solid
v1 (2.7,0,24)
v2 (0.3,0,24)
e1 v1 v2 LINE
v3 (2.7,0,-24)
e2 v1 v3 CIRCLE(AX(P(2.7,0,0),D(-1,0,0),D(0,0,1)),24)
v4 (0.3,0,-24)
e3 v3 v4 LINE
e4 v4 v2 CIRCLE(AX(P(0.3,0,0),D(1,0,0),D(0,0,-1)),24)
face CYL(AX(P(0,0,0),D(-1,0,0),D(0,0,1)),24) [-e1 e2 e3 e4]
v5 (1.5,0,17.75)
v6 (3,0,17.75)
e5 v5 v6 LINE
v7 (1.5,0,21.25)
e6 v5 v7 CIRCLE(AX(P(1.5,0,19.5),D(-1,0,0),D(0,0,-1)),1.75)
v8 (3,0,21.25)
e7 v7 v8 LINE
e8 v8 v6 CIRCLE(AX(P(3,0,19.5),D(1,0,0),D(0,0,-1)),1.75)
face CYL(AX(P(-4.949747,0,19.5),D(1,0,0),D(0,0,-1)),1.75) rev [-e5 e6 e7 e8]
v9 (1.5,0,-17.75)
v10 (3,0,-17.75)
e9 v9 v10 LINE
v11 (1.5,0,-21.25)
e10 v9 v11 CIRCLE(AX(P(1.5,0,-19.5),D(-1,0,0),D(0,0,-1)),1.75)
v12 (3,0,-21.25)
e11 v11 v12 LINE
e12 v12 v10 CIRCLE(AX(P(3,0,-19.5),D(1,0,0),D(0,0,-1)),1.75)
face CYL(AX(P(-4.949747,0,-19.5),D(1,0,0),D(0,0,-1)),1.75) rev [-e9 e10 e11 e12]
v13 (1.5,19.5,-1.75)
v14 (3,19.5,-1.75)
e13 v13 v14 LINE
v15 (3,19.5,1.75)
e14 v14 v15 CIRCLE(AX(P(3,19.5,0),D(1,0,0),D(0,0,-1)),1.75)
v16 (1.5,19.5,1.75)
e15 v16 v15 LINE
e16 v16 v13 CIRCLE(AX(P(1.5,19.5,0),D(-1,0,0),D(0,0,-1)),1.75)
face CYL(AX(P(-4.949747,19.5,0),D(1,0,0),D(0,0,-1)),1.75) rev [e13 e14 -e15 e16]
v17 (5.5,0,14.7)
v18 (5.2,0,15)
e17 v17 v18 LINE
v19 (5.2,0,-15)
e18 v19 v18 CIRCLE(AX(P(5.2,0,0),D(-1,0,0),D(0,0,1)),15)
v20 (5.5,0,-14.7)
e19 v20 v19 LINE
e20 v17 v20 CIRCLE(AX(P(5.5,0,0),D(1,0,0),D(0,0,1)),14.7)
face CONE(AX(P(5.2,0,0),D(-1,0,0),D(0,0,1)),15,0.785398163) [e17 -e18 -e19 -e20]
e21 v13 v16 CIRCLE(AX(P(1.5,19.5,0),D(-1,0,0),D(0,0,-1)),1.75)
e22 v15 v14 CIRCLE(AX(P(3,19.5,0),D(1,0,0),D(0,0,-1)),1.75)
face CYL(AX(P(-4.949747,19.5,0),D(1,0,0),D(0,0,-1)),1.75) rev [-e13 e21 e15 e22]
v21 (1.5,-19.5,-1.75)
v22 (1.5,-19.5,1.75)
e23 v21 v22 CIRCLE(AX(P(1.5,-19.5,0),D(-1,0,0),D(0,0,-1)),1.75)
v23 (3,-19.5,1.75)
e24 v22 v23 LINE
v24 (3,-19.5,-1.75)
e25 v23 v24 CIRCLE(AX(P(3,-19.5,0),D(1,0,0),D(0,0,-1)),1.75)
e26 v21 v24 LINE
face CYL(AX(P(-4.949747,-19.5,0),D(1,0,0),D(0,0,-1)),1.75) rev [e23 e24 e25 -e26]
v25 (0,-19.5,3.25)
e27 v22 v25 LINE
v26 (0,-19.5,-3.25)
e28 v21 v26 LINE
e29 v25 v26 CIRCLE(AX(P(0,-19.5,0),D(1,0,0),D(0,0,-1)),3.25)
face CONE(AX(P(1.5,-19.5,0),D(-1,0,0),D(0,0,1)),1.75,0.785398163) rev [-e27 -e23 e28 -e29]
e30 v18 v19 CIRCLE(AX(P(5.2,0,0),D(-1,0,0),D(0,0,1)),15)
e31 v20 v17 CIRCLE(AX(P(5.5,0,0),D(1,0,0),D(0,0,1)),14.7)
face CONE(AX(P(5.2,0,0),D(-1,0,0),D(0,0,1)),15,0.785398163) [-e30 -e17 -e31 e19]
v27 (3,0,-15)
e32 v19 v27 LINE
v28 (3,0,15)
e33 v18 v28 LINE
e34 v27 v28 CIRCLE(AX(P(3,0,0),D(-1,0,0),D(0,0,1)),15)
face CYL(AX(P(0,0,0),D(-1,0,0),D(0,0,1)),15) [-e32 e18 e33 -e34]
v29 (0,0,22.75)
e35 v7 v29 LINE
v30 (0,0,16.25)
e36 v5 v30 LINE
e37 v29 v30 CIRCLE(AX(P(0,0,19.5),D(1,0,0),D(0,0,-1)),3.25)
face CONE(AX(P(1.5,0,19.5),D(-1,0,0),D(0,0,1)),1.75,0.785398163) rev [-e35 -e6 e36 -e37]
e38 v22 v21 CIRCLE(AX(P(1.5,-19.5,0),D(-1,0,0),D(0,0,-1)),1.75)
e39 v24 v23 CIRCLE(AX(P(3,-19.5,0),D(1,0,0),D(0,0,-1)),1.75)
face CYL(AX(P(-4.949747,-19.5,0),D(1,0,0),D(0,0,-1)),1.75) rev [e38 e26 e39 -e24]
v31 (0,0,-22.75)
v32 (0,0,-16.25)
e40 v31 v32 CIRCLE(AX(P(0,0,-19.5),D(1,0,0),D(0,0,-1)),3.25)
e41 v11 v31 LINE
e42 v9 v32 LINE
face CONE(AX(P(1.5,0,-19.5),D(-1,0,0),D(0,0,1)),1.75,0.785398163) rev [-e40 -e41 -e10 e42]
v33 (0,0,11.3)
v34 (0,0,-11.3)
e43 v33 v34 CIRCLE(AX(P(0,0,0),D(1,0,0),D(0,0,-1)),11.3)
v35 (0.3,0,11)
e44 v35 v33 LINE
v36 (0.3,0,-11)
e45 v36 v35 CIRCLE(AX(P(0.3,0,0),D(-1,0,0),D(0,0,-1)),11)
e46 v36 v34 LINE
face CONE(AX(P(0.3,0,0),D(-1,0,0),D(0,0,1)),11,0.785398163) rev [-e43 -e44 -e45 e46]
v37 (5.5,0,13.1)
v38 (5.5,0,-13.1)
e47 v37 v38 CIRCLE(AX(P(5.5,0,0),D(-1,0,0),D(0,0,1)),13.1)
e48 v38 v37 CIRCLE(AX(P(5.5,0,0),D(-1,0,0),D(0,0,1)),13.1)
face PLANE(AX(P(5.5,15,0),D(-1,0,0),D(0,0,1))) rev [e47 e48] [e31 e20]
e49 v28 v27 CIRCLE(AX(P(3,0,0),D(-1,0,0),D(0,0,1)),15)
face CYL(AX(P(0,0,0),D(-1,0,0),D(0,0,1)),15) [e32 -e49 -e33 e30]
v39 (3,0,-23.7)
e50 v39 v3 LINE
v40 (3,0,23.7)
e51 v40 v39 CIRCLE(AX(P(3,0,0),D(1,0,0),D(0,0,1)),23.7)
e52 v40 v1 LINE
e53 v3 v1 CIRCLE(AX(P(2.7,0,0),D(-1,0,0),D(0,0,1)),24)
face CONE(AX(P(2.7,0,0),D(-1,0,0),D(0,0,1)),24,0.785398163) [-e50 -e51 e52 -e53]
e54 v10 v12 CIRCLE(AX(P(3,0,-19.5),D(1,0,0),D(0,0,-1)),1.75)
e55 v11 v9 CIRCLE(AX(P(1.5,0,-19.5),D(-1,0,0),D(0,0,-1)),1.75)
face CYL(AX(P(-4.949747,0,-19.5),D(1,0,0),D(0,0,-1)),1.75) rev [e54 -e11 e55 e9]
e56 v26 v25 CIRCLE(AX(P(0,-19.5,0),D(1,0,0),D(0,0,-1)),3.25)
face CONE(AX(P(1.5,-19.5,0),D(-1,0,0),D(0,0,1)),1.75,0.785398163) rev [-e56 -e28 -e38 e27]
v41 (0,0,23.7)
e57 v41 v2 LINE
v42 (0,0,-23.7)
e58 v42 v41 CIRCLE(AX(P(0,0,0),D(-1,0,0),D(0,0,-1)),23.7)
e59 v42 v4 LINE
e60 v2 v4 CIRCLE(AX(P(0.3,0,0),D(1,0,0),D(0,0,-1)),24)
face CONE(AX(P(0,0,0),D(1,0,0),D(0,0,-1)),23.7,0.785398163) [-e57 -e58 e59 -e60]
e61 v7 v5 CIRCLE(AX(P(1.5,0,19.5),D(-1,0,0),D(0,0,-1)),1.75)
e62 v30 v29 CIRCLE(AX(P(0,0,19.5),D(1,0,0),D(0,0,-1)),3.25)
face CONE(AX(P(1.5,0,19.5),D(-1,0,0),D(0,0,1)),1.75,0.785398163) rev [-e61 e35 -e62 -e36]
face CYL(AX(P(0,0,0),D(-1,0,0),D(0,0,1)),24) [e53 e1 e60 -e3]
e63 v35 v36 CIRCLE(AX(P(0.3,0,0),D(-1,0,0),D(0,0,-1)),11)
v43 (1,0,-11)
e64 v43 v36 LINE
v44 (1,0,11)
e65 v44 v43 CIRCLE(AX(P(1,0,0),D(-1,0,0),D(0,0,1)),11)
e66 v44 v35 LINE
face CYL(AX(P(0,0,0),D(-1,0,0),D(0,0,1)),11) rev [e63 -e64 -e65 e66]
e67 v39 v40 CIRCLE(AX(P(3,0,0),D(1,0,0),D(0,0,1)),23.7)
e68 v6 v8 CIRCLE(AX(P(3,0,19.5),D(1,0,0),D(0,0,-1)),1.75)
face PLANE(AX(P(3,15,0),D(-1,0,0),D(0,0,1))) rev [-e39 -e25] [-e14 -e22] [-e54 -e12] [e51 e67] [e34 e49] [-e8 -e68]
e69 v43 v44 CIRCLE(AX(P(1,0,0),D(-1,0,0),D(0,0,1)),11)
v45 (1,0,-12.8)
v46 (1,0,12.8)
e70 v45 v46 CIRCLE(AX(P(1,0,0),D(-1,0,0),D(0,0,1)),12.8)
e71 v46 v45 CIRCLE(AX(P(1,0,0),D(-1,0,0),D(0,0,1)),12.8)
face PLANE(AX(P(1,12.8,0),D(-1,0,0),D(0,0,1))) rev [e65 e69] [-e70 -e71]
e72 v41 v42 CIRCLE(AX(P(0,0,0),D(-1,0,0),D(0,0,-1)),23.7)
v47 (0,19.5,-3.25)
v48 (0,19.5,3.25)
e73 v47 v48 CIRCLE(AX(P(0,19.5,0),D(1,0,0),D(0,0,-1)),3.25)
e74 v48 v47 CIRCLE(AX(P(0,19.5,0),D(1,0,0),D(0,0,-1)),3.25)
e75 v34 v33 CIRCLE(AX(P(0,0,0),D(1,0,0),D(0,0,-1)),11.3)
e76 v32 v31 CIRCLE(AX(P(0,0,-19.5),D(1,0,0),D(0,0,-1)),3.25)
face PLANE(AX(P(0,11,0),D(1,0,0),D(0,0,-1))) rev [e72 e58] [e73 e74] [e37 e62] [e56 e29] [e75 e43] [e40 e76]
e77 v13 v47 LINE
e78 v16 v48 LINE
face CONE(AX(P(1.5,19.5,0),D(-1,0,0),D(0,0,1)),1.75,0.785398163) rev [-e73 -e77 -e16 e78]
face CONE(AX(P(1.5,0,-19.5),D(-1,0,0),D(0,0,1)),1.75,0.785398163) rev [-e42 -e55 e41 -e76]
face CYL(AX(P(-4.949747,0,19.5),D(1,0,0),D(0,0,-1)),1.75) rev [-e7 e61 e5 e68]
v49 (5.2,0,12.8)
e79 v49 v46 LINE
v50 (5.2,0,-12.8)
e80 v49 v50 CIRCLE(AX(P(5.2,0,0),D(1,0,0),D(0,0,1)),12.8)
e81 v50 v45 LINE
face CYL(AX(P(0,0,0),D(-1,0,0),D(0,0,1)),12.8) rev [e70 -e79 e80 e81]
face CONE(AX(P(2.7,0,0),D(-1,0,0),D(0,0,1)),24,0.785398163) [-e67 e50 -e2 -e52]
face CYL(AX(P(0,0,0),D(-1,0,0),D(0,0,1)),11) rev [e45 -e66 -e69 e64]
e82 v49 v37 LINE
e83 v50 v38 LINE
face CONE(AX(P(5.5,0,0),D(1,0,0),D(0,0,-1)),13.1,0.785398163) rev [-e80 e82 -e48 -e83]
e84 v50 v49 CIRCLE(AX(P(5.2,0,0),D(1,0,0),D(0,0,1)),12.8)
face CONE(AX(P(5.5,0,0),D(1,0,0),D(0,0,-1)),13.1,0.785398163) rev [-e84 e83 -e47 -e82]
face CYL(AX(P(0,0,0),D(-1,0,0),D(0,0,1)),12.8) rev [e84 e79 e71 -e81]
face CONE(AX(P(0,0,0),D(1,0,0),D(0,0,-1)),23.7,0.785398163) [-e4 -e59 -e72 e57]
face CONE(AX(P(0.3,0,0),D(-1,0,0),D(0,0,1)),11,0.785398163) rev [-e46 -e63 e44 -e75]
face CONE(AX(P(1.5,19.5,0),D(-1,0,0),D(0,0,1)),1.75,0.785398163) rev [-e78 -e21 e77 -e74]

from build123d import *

# Parameters (mm, degrees)
SKETCH2_R          = 1.75
CUT_EXTRUDE1_DEPTH = 3
CHAMFER1_SIZE      = 1.5
CHAMFER2_SIZE      = 0.3


with BuildPart() as part:
    # Sketch1 → Revolve1 (revolve)
    with BuildSketch(Plane.XY, mode=Mode.PRIVATE) as revolve1_sk:
        Polygon((0, 11), (0, 24), (3, 24), (3, 15), (5.5, 15), (5.5, 12.8), (1, 12.8), (1, 11), align=None)
    revolve(revolve1_sk.sketch.rotate(Axis((0, 0, 0), (1, 0, 0)), 90), axis=Axis((0, 0, 0), (1, 0, 0)))

    # Sketch2 → Cut-Extrude1 (cut)
    with BuildSketch(Plane(origin=(3, 0, 0), x_dir=(0, 0, -1), z_dir=(1, 0, 0))):
        with Locations((0, 19.5)):
            Circle(SKETCH2_R)
        with Locations((19.5, 0)):
            Circle(SKETCH2_R)
        with Locations((0, -19.5)):
            Circle(SKETCH2_R)
        with Locations((-19.5, 0)):
            Circle(SKETCH2_R)
    extrude(amount=-CUT_EXTRUDE1_DEPTH, mode=Mode.SUBTRACT)

    # Chamfer1
    chamfer1_edges = [part.edges().sort_by_distance(p)[0] for p in [
        (0, 19.5, 1.75),
        (0, 0, -17.75),
        (0, -19.5, 1.75),
        (0, 0, 21.25),
    ]]
    chamfer(chamfer1_edges, length=CHAMFER1_SIZE)

    # Chamfer2
    chamfer2_edges = [part.edges().sort_by_distance(p)[0] for p in [
        (3, 0, -24),
        (0, 0, -24),
        (0, 0, -11),
        (5.5, 0, -12.8),
        (5.5, 0, -15),
    ]]
    chamfer(chamfer2_edges, length=CHAMFER2_SIZE)


solid = part.part
